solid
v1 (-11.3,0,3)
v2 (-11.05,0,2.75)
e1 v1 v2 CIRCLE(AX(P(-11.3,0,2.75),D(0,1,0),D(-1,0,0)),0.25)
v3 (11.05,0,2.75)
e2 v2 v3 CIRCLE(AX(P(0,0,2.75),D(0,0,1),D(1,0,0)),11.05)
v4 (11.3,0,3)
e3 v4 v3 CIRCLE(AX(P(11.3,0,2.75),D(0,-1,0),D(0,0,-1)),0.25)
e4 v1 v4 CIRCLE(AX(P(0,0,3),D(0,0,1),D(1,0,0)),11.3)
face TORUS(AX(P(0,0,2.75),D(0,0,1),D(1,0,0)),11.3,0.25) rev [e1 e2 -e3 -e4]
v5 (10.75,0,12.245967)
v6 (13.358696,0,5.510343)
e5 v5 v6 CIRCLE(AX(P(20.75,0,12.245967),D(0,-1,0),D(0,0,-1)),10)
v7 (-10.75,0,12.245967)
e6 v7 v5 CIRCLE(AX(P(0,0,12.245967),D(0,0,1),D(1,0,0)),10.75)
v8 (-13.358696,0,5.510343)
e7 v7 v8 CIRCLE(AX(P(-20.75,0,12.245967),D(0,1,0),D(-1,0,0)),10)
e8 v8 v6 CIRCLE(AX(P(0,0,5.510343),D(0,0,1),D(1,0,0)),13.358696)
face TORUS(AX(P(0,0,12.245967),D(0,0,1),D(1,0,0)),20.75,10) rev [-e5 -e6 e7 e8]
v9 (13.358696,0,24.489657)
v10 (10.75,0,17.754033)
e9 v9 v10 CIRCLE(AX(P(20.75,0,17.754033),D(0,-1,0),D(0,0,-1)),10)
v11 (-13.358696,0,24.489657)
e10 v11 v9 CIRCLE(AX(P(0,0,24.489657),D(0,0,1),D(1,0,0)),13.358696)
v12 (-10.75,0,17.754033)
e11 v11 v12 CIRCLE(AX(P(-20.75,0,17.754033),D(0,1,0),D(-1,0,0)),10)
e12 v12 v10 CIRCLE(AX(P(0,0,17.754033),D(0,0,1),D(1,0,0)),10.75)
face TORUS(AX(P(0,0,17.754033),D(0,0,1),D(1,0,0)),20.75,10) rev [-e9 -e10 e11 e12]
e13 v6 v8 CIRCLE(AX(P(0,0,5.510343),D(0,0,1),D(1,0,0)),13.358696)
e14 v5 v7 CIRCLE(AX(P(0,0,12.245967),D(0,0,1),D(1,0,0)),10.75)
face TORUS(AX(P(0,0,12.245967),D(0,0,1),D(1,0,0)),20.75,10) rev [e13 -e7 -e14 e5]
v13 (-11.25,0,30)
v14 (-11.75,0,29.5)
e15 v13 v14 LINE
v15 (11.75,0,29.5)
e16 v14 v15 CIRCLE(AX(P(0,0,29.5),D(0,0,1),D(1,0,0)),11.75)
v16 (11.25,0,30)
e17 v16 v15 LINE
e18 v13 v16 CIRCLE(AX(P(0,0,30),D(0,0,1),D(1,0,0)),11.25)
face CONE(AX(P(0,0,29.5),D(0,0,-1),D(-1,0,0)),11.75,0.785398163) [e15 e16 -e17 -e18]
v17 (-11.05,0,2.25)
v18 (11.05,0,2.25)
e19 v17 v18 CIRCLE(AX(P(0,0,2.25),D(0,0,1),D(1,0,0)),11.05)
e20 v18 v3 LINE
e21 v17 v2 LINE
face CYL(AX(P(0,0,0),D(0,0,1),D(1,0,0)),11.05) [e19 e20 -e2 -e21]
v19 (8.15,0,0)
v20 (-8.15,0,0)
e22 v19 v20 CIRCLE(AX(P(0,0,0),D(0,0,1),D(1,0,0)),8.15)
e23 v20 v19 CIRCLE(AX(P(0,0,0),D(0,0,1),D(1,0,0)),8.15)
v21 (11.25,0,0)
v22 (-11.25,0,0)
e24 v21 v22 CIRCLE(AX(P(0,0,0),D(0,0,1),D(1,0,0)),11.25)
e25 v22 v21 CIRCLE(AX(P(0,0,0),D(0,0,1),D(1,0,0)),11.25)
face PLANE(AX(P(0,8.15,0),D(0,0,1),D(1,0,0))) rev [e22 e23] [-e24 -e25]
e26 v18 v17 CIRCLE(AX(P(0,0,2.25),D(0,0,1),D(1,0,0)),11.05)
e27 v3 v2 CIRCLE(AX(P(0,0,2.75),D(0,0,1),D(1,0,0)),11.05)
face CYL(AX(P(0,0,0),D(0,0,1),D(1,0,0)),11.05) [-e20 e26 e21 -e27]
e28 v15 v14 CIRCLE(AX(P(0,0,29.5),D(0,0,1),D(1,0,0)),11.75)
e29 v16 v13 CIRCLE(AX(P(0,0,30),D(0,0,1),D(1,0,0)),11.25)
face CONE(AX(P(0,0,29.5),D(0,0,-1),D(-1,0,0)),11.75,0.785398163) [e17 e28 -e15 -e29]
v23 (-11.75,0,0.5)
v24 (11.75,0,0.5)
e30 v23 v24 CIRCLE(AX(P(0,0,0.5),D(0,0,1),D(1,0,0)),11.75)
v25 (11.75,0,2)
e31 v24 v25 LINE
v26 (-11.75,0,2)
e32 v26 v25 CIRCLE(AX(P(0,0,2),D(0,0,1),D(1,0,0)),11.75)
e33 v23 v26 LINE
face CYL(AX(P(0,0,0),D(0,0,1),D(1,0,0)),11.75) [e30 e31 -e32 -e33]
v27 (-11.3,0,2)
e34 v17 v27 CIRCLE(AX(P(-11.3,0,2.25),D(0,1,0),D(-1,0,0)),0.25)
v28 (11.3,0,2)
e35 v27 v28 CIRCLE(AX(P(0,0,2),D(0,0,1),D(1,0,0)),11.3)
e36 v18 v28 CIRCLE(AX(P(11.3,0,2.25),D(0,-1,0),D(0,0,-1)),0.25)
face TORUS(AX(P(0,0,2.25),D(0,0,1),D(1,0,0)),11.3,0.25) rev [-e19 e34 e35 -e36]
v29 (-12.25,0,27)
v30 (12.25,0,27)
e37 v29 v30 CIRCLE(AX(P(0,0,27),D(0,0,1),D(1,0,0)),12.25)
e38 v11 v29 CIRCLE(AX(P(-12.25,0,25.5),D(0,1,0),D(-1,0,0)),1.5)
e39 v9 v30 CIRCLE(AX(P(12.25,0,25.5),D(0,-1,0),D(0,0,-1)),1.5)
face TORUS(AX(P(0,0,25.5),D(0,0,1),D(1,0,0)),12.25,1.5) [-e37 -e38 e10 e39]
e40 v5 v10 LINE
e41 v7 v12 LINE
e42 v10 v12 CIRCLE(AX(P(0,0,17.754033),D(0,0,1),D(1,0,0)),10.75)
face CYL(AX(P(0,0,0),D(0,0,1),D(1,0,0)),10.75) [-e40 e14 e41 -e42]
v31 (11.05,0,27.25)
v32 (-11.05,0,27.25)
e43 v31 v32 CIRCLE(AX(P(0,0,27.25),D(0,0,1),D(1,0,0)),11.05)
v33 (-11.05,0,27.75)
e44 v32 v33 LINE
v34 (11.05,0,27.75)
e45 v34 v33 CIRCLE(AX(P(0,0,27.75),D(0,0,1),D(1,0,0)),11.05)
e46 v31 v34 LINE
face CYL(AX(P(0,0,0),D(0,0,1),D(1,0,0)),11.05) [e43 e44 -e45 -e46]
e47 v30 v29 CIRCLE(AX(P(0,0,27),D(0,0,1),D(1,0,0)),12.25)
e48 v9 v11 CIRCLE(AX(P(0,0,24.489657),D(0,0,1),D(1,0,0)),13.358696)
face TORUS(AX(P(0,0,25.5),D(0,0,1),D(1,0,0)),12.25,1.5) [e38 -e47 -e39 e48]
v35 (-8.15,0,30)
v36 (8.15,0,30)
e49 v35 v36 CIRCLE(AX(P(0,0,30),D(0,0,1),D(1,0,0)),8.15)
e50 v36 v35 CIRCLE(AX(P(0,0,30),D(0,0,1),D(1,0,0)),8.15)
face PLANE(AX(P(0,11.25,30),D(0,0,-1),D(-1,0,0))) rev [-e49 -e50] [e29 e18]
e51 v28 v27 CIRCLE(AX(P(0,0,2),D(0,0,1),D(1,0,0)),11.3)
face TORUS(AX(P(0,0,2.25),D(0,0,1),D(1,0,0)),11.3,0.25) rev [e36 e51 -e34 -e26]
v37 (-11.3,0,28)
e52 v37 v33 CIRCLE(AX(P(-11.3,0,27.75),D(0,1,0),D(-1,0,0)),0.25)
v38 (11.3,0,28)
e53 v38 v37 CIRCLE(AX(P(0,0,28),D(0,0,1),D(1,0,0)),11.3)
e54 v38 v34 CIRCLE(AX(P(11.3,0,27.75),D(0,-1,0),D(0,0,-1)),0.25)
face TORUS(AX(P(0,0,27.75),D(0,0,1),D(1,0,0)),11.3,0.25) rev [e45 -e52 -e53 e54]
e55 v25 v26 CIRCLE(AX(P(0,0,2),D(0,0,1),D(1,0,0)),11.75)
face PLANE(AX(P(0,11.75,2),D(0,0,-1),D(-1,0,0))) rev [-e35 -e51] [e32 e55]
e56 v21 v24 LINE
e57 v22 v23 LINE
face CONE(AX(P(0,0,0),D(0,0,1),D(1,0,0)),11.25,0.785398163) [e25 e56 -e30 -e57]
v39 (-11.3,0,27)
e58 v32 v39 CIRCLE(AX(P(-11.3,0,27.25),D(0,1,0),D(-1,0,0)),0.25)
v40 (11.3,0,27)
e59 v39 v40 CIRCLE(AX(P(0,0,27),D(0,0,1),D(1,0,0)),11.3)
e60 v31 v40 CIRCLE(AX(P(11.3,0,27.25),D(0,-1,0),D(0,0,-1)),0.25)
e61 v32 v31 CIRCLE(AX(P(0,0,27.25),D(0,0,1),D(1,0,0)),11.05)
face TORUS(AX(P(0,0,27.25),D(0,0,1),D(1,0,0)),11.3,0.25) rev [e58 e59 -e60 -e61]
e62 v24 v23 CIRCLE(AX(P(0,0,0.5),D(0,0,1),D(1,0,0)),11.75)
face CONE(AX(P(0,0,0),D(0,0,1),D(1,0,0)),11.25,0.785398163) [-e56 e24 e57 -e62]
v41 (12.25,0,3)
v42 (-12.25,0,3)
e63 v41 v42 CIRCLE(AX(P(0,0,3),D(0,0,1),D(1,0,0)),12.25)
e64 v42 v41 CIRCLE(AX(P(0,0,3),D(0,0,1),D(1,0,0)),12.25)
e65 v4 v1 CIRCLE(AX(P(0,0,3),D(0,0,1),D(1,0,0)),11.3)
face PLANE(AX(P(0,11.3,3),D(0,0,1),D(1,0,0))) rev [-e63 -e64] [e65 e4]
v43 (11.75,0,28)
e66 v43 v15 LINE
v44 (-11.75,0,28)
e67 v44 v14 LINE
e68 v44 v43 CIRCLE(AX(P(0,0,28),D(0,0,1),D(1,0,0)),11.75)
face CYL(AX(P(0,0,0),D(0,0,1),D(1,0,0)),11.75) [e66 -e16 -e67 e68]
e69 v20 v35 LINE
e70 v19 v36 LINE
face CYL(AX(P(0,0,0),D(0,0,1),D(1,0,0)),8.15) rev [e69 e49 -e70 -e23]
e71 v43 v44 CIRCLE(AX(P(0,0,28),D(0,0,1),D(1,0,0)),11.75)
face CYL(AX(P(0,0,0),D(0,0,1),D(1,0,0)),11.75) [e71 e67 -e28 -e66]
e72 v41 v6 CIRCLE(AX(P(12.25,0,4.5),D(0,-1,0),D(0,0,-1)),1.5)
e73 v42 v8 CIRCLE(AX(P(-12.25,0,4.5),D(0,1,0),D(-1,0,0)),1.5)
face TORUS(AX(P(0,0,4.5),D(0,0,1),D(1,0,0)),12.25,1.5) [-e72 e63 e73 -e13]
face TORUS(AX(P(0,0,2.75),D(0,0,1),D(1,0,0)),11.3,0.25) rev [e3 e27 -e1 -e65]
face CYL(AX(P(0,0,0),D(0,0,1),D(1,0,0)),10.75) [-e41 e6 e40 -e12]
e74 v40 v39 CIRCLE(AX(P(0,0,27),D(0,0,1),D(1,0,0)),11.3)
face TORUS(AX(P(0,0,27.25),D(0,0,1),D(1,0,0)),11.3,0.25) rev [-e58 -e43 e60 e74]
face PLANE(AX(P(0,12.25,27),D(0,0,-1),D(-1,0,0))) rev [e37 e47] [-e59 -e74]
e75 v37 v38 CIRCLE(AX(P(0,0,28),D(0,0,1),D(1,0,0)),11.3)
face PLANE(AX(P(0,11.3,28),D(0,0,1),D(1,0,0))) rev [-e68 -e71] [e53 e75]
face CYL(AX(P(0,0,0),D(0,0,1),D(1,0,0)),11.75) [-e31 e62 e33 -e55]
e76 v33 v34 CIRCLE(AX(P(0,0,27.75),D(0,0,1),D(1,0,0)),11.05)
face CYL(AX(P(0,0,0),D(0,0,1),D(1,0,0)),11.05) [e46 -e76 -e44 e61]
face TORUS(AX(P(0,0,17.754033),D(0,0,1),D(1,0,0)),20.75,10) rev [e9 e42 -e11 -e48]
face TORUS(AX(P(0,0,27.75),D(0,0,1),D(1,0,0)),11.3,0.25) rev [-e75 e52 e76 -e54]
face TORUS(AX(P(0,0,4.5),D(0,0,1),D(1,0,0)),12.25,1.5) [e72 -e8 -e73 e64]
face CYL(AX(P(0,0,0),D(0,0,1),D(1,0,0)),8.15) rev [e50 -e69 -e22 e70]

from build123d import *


with BuildPart() as part:
    # 草图1 → 旋转1 (revolve)
    with BuildSketch(Plane(origin=(0, 0, 0), x_dir=(0, 0, -1), z_dir=(1, 0, 0)), mode=Mode.PRIVATE) as revolve_1_sk:
        with BuildLine():
            Line((-30, 11.25), (-30, 8.15))
            Line((-30, 8.15), (0, 8.15))
            Line((0, 8.15), (0, 11.25))
            Line((0, 11.25), (-0.5, 11.75))
            Line((-0.5, 11.75), (-2, 11.75))
            Line((-2, 11.75), (-2, 11.3))
            ThreePointArc((-2, 11.3), (-2.073223305, 11.123223305), (-2.25, 11.05))
            Line((-2.25, 11.05), (-2.75, 11.05))
            ThreePointArc((-2.75, 11.05), (-2.926776695, 11.123223305), (-3, 11.3))
            Line((-3, 11.3), (-3, 12.25))
            ThreePointArc((-3, 12.25), (-3.893994729, 13.622136149), (-5.510343482, 13.358695652))
            ThreePointArc((-5.510343482, 13.358695652), (-8.6343911, 11.424951918), (-12.245966692, 10.75))
            Line((-12.245966692, 10.75), (-17.754033308, 10.75))
            ThreePointArc((-17.754033308, 10.75), (-21.3656089, 11.424951918), (-24.489656518, 13.358695652))
            ThreePointArc((-24.489656518, 13.358695652), (-26.106005271, 13.622136149), (-27, 12.25))
            Line((-27, 12.25), (-27, 11.3))
            ThreePointArc((-27, 11.3), (-27.073223305, 11.123223305), (-27.25, 11.05))
            Line((-27.25, 11.05), (-27.75, 11.05))
            ThreePointArc((-27.75, 11.05), (-27.926776695, 11.123223305), (-28, 11.3))
            Line((-28, 11.3), (-28, 11.75))
            Line((-28, 11.75), (-29.5, 11.75))
            Line((-29.5, 11.75), (-30, 11.25))
        make_face()
    revolve(revolve_1_sk.sketch.rotate(Axis((0, 0, 0), (0, 0, 1)), 270), axis=Axis((0, 0, 0), (0, 0, 1)))


solid = part.part
